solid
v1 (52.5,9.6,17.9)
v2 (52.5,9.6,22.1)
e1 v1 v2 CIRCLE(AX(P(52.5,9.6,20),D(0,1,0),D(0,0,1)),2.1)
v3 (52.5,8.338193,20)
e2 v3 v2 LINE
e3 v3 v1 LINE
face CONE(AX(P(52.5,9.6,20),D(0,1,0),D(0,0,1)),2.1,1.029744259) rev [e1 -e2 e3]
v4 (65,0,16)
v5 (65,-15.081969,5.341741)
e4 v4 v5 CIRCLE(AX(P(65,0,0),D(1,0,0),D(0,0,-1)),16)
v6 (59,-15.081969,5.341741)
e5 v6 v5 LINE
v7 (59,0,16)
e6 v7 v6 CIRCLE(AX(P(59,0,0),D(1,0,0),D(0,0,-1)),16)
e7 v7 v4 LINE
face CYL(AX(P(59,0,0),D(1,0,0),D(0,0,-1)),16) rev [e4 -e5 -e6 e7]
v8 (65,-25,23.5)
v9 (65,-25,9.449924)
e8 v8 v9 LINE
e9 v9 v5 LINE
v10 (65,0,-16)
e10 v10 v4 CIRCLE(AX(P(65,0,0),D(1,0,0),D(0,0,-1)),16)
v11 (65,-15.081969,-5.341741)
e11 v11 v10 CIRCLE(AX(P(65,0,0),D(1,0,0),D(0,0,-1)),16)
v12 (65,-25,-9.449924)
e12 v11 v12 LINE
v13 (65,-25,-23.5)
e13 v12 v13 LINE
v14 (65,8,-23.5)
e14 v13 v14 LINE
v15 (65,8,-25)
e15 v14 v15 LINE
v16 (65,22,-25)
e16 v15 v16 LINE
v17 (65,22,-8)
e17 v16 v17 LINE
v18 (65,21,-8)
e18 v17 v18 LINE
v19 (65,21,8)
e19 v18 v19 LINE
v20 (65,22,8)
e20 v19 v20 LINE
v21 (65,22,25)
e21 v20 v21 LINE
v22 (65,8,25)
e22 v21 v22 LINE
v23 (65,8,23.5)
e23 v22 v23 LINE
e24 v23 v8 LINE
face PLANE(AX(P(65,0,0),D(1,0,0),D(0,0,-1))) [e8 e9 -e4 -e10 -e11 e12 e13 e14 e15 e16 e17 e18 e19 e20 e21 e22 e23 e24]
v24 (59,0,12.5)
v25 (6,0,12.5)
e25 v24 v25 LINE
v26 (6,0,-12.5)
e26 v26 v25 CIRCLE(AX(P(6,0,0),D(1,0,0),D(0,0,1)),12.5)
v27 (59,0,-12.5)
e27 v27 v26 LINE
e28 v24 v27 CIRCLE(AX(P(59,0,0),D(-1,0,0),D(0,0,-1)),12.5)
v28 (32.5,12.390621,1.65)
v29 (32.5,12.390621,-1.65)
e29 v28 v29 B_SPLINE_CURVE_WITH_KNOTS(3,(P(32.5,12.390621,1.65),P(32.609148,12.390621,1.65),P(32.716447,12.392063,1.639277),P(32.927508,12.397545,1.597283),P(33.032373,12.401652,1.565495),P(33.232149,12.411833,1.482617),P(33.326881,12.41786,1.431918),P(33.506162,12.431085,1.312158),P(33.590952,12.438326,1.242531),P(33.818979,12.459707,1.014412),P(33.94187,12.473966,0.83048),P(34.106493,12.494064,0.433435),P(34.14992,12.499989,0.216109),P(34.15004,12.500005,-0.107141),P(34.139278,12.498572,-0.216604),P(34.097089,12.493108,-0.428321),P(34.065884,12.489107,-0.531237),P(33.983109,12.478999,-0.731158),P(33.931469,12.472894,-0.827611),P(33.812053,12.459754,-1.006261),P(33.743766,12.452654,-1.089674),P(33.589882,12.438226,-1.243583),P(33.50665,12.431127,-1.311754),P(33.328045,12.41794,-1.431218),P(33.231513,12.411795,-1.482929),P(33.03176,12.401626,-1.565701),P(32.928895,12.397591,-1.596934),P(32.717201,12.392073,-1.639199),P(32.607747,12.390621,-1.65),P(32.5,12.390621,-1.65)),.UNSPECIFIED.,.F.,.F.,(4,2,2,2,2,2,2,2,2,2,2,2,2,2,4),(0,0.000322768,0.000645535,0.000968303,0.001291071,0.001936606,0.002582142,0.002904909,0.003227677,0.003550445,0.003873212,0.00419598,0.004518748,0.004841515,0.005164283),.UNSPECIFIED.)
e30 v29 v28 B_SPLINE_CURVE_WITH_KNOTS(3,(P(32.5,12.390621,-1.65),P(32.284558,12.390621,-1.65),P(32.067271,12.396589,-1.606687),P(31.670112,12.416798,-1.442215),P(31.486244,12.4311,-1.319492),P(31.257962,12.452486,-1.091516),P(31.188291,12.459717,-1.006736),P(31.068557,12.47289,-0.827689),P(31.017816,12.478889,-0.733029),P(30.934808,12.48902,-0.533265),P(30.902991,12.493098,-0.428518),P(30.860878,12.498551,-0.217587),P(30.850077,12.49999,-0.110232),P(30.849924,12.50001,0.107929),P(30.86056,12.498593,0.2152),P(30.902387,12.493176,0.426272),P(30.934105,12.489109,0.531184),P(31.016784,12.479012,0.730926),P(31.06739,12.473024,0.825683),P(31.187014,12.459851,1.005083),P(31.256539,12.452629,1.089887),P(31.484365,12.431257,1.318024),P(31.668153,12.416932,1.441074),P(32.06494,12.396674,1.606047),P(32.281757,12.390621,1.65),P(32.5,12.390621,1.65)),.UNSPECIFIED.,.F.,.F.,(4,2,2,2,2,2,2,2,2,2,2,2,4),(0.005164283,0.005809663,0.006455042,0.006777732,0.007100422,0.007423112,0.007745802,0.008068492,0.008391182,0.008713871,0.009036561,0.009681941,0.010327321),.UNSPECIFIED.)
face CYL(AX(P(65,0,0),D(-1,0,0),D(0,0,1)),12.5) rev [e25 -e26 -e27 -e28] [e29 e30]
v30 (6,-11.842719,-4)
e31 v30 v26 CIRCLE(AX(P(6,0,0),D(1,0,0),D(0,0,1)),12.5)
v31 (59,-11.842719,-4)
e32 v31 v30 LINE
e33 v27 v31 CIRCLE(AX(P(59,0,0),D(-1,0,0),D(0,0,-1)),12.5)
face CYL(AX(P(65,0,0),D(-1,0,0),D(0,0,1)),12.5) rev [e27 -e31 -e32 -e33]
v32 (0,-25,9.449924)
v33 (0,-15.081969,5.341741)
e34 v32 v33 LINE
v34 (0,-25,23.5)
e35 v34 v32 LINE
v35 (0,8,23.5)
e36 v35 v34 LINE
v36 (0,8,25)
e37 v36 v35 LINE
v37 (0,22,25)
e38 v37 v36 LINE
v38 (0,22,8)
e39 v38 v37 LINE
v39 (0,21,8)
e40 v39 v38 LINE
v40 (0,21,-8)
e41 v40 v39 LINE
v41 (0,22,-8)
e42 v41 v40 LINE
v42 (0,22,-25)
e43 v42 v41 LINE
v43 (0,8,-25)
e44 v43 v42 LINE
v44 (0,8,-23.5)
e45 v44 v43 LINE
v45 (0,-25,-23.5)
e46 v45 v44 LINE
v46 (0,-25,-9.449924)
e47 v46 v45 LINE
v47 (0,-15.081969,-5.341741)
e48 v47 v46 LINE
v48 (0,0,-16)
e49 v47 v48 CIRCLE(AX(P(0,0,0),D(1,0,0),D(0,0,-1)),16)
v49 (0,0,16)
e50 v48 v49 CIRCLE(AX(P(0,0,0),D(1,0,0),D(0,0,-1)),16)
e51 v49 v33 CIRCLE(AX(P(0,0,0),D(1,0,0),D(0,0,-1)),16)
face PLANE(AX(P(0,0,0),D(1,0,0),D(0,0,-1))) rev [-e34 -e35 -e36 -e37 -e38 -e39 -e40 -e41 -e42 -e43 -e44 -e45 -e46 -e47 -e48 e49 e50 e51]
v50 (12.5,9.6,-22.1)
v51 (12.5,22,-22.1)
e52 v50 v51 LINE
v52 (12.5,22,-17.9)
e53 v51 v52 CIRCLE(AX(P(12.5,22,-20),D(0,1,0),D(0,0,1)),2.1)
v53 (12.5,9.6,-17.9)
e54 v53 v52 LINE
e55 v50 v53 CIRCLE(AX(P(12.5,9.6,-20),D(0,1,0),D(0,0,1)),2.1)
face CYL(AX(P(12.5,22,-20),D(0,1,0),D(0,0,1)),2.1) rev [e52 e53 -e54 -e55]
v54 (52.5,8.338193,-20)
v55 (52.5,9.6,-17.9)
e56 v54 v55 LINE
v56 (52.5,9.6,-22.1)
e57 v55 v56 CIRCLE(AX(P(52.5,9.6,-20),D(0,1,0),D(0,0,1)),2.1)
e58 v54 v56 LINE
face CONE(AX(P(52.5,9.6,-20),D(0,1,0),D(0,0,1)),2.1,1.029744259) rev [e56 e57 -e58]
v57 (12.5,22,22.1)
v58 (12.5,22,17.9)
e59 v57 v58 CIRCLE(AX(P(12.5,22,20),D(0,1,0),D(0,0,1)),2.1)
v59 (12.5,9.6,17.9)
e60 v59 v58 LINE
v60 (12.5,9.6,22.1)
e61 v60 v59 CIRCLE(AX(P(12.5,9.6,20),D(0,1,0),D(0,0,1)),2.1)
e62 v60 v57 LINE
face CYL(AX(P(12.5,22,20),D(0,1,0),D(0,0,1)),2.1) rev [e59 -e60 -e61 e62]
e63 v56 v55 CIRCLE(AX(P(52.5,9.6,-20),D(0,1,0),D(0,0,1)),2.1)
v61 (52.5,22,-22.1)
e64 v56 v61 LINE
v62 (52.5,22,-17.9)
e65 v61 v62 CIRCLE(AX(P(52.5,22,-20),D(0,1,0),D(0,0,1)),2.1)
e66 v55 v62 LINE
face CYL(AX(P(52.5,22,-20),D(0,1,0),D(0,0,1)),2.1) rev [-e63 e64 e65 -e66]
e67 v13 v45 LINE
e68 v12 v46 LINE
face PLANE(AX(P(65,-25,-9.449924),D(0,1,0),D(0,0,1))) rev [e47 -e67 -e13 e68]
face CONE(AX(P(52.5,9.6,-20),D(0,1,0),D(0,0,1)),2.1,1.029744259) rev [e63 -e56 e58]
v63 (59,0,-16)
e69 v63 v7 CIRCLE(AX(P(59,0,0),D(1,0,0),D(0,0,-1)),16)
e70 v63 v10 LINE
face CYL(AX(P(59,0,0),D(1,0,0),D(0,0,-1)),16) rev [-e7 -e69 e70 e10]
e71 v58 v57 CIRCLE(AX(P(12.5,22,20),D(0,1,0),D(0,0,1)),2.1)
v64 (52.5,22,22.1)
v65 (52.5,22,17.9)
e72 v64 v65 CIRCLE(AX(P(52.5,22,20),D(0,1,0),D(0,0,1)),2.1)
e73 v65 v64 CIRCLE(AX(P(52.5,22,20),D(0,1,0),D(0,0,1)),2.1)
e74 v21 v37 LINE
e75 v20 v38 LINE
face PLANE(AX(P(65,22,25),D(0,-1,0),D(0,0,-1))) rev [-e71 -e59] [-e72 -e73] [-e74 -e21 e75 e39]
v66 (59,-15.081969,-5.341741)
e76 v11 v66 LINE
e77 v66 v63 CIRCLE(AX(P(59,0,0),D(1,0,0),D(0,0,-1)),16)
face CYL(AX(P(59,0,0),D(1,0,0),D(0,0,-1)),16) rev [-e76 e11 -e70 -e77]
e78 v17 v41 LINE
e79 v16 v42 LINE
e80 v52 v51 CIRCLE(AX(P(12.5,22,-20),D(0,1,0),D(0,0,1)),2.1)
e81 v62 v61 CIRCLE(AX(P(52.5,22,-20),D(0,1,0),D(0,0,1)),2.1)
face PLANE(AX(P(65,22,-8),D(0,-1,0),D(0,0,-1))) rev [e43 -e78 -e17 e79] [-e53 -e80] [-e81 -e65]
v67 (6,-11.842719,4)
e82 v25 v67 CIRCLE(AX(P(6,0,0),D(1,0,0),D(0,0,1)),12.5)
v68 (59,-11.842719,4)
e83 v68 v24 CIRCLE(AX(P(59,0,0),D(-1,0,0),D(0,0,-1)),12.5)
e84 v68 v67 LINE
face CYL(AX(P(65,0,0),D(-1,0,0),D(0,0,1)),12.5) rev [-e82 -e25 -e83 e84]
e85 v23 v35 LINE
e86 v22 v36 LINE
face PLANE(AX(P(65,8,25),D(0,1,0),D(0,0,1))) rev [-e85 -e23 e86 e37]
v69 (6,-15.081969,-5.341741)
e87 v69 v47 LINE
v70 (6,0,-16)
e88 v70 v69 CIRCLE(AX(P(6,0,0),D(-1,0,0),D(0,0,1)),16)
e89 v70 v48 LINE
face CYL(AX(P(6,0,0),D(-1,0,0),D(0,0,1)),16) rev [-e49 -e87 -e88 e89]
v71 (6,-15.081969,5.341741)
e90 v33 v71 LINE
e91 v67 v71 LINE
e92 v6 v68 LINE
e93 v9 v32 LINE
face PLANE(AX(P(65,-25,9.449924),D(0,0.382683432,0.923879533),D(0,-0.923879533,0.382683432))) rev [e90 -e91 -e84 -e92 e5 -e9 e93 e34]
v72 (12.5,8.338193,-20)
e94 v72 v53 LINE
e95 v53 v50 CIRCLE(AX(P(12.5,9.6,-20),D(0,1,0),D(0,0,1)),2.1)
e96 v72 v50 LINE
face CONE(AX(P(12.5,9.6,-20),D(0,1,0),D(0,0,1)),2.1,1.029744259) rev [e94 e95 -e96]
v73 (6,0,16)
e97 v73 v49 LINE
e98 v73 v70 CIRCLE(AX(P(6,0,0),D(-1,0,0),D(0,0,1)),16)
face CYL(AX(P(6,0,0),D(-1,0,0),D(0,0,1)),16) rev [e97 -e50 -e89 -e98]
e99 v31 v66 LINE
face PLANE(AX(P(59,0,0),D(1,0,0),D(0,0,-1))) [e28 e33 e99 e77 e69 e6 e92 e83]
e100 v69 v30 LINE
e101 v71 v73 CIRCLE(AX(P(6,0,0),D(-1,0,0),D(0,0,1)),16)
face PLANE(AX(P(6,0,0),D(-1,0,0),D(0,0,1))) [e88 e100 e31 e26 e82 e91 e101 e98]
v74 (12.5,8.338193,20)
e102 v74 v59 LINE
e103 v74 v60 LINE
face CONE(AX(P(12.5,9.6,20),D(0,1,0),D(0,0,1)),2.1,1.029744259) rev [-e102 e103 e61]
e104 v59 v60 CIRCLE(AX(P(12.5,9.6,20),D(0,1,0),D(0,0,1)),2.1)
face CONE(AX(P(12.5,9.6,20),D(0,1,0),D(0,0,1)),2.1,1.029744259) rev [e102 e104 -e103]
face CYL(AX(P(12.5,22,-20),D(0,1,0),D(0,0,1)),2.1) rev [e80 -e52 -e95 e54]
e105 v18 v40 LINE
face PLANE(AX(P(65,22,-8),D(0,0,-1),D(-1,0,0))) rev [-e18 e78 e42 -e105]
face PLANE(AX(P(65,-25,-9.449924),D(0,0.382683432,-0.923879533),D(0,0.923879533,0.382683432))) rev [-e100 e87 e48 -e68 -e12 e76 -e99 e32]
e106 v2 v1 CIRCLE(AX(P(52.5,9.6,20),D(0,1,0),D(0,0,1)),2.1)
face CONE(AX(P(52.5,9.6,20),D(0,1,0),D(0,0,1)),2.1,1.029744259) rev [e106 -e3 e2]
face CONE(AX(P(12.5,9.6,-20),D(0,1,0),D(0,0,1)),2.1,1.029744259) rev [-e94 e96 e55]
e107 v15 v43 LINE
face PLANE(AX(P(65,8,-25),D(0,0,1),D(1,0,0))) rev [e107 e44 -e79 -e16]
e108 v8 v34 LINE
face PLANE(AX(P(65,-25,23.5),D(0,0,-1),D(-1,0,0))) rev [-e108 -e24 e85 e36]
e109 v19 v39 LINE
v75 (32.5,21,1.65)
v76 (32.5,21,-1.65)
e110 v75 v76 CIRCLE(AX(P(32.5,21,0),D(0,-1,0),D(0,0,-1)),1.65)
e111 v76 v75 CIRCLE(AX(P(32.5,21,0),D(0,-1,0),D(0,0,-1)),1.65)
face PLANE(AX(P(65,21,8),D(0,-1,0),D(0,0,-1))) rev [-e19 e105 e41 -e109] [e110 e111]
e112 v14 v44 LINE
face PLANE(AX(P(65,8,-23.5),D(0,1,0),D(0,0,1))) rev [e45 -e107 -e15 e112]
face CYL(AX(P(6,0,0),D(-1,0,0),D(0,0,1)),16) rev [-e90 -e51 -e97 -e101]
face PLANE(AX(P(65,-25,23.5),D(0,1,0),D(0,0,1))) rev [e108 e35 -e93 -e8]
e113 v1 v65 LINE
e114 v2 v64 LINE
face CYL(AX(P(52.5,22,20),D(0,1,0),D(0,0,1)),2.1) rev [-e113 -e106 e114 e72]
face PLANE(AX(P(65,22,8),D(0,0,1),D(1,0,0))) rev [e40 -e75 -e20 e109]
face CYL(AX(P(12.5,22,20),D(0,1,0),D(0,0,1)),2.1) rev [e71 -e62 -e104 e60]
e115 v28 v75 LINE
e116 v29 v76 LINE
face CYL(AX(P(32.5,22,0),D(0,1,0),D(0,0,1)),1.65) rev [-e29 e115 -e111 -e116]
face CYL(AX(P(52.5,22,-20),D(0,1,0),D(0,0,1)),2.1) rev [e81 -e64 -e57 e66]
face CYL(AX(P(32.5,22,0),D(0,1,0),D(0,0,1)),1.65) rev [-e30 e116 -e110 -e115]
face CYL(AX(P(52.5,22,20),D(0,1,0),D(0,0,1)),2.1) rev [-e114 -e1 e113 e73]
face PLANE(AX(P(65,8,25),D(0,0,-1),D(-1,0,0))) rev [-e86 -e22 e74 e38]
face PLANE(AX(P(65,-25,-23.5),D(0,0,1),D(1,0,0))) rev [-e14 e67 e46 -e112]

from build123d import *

# Parameters (mm, degrees)
EXTRUDE1_DEPTH            = 65
SKETCH2_R                 = 16
EXTRUDE2_DEPTH            = 6
EXTRUDE3_START            = -6
SKETCH3_R                 = 16
EXTRUDE3_DEPTH            = 6
M5X0_8_TAPPED_HOLE1_D     = 4.2
M5X0_8_TAPPED_HOLE1_DEPTH = 12.4
M5X0_8_TAPPED_HOLE1_TIP   = 1.2618073
M4X0_7_TAPPED_HOLE1_D     = 3.3
M4X0_7_TAPPED_HOLE1_DEPTH = 10.1
M4X0_7_TAPPED_HOLE1_TIP   = 0.991420021


with BuildPart() as part:
    # Sketch1 → Extrude1 (new body)
    with BuildSketch(Plane(origin=(0, 0, 0), x_dir=(0, 0, -1), z_dir=(1, 0, 0))):
        with BuildLine():
            Line((-23.5, -25), (-9.449924117, -25))
            Line((-9.449924117, -25), (-4, -11.842719282))
            ThreePointArc((-4, -11.842719282), (0, 12.5), (4, -11.842719282))
            Line((4, -11.842719282), (9.449924117, -25))
            Line((9.449924117, -25), (23.5, -25))
            Line((23.5, -25), (23.5, 8))
            Line((23.5, 8), (25, 8))
            Line((25, 8), (25, 22))
            Line((25, 22), (8, 22))
            Line((8, 22), (8, 21))
            Line((8, 21), (-8, 21))
            Line((-8, 21), (-8, 22))
            Line((-8, 22), (-25, 22))
            Line((-25, 22), (-25, 8))
            Line((-25, 8), (-23.5, 8))
            Line((-23.5, 8), (-23.5, -25))
        make_face()
    extrude(amount=EXTRUDE1_DEPTH)

    # Sketch2 → Extrude2 (cut)
    with BuildSketch(Plane(origin=(65, 0, 0), x_dir=(0, 0, -1), z_dir=(1, 0, 0))):
        Circle(SKETCH2_R)
    extrude(amount=-EXTRUDE2_DEPTH, mode=Mode.SUBTRACT)

    # Sketch3 → Extrude3 (cut)
    with BuildSketch(Plane.ZY.offset(EXTRUDE3_START)):
        Circle(SKETCH3_R)
    extrude(amount=EXTRUDE3_DEPTH, mode=Mode.SUBTRACT)

    # M5x0.8 Tapped Hole1
    with Locations(Plane(origin=(12.5, 22, -20), x_dir=(0, 0, 1), z_dir=(0, 1, 0))):
        with Locations((0, 0), (0, 40), (40, 0), (40, 40)):
            Hole(M5X0_8_TAPPED_HOLE1_D / 2, depth=M5X0_8_TAPPED_HOLE1_DEPTH)
            with Locations((0, 0, -(M5X0_8_TAPPED_HOLE1_DEPTH + M5X0_8_TAPPED_HOLE1_TIP / 2))):  # 118° drill point
                Cone(0, M5X0_8_TAPPED_HOLE1_D / 2, M5X0_8_TAPPED_HOLE1_TIP, mode=Mode.SUBTRACT)

    # M4x0.7 Tapped Hole1
    with Locations(Plane(origin=(32.5, 22, 0), x_dir=(0, 0, 1), z_dir=(0, 1, 0))):
        with Locations((0, 0)):
            Hole(M4X0_7_TAPPED_HOLE1_D / 2, depth=M4X0_7_TAPPED_HOLE1_DEPTH)
            with Locations((0, 0, -(M4X0_7_TAPPED_HOLE1_DEPTH + M4X0_7_TAPPED_HOLE1_TIP / 2))):  # 118° drill point
                Cone(0, M4X0_7_TAPPED_HOLE1_D / 2, M4X0_7_TAPPED_HOLE1_TIP, mode=Mode.SUBTRACT)


solid = part.part
